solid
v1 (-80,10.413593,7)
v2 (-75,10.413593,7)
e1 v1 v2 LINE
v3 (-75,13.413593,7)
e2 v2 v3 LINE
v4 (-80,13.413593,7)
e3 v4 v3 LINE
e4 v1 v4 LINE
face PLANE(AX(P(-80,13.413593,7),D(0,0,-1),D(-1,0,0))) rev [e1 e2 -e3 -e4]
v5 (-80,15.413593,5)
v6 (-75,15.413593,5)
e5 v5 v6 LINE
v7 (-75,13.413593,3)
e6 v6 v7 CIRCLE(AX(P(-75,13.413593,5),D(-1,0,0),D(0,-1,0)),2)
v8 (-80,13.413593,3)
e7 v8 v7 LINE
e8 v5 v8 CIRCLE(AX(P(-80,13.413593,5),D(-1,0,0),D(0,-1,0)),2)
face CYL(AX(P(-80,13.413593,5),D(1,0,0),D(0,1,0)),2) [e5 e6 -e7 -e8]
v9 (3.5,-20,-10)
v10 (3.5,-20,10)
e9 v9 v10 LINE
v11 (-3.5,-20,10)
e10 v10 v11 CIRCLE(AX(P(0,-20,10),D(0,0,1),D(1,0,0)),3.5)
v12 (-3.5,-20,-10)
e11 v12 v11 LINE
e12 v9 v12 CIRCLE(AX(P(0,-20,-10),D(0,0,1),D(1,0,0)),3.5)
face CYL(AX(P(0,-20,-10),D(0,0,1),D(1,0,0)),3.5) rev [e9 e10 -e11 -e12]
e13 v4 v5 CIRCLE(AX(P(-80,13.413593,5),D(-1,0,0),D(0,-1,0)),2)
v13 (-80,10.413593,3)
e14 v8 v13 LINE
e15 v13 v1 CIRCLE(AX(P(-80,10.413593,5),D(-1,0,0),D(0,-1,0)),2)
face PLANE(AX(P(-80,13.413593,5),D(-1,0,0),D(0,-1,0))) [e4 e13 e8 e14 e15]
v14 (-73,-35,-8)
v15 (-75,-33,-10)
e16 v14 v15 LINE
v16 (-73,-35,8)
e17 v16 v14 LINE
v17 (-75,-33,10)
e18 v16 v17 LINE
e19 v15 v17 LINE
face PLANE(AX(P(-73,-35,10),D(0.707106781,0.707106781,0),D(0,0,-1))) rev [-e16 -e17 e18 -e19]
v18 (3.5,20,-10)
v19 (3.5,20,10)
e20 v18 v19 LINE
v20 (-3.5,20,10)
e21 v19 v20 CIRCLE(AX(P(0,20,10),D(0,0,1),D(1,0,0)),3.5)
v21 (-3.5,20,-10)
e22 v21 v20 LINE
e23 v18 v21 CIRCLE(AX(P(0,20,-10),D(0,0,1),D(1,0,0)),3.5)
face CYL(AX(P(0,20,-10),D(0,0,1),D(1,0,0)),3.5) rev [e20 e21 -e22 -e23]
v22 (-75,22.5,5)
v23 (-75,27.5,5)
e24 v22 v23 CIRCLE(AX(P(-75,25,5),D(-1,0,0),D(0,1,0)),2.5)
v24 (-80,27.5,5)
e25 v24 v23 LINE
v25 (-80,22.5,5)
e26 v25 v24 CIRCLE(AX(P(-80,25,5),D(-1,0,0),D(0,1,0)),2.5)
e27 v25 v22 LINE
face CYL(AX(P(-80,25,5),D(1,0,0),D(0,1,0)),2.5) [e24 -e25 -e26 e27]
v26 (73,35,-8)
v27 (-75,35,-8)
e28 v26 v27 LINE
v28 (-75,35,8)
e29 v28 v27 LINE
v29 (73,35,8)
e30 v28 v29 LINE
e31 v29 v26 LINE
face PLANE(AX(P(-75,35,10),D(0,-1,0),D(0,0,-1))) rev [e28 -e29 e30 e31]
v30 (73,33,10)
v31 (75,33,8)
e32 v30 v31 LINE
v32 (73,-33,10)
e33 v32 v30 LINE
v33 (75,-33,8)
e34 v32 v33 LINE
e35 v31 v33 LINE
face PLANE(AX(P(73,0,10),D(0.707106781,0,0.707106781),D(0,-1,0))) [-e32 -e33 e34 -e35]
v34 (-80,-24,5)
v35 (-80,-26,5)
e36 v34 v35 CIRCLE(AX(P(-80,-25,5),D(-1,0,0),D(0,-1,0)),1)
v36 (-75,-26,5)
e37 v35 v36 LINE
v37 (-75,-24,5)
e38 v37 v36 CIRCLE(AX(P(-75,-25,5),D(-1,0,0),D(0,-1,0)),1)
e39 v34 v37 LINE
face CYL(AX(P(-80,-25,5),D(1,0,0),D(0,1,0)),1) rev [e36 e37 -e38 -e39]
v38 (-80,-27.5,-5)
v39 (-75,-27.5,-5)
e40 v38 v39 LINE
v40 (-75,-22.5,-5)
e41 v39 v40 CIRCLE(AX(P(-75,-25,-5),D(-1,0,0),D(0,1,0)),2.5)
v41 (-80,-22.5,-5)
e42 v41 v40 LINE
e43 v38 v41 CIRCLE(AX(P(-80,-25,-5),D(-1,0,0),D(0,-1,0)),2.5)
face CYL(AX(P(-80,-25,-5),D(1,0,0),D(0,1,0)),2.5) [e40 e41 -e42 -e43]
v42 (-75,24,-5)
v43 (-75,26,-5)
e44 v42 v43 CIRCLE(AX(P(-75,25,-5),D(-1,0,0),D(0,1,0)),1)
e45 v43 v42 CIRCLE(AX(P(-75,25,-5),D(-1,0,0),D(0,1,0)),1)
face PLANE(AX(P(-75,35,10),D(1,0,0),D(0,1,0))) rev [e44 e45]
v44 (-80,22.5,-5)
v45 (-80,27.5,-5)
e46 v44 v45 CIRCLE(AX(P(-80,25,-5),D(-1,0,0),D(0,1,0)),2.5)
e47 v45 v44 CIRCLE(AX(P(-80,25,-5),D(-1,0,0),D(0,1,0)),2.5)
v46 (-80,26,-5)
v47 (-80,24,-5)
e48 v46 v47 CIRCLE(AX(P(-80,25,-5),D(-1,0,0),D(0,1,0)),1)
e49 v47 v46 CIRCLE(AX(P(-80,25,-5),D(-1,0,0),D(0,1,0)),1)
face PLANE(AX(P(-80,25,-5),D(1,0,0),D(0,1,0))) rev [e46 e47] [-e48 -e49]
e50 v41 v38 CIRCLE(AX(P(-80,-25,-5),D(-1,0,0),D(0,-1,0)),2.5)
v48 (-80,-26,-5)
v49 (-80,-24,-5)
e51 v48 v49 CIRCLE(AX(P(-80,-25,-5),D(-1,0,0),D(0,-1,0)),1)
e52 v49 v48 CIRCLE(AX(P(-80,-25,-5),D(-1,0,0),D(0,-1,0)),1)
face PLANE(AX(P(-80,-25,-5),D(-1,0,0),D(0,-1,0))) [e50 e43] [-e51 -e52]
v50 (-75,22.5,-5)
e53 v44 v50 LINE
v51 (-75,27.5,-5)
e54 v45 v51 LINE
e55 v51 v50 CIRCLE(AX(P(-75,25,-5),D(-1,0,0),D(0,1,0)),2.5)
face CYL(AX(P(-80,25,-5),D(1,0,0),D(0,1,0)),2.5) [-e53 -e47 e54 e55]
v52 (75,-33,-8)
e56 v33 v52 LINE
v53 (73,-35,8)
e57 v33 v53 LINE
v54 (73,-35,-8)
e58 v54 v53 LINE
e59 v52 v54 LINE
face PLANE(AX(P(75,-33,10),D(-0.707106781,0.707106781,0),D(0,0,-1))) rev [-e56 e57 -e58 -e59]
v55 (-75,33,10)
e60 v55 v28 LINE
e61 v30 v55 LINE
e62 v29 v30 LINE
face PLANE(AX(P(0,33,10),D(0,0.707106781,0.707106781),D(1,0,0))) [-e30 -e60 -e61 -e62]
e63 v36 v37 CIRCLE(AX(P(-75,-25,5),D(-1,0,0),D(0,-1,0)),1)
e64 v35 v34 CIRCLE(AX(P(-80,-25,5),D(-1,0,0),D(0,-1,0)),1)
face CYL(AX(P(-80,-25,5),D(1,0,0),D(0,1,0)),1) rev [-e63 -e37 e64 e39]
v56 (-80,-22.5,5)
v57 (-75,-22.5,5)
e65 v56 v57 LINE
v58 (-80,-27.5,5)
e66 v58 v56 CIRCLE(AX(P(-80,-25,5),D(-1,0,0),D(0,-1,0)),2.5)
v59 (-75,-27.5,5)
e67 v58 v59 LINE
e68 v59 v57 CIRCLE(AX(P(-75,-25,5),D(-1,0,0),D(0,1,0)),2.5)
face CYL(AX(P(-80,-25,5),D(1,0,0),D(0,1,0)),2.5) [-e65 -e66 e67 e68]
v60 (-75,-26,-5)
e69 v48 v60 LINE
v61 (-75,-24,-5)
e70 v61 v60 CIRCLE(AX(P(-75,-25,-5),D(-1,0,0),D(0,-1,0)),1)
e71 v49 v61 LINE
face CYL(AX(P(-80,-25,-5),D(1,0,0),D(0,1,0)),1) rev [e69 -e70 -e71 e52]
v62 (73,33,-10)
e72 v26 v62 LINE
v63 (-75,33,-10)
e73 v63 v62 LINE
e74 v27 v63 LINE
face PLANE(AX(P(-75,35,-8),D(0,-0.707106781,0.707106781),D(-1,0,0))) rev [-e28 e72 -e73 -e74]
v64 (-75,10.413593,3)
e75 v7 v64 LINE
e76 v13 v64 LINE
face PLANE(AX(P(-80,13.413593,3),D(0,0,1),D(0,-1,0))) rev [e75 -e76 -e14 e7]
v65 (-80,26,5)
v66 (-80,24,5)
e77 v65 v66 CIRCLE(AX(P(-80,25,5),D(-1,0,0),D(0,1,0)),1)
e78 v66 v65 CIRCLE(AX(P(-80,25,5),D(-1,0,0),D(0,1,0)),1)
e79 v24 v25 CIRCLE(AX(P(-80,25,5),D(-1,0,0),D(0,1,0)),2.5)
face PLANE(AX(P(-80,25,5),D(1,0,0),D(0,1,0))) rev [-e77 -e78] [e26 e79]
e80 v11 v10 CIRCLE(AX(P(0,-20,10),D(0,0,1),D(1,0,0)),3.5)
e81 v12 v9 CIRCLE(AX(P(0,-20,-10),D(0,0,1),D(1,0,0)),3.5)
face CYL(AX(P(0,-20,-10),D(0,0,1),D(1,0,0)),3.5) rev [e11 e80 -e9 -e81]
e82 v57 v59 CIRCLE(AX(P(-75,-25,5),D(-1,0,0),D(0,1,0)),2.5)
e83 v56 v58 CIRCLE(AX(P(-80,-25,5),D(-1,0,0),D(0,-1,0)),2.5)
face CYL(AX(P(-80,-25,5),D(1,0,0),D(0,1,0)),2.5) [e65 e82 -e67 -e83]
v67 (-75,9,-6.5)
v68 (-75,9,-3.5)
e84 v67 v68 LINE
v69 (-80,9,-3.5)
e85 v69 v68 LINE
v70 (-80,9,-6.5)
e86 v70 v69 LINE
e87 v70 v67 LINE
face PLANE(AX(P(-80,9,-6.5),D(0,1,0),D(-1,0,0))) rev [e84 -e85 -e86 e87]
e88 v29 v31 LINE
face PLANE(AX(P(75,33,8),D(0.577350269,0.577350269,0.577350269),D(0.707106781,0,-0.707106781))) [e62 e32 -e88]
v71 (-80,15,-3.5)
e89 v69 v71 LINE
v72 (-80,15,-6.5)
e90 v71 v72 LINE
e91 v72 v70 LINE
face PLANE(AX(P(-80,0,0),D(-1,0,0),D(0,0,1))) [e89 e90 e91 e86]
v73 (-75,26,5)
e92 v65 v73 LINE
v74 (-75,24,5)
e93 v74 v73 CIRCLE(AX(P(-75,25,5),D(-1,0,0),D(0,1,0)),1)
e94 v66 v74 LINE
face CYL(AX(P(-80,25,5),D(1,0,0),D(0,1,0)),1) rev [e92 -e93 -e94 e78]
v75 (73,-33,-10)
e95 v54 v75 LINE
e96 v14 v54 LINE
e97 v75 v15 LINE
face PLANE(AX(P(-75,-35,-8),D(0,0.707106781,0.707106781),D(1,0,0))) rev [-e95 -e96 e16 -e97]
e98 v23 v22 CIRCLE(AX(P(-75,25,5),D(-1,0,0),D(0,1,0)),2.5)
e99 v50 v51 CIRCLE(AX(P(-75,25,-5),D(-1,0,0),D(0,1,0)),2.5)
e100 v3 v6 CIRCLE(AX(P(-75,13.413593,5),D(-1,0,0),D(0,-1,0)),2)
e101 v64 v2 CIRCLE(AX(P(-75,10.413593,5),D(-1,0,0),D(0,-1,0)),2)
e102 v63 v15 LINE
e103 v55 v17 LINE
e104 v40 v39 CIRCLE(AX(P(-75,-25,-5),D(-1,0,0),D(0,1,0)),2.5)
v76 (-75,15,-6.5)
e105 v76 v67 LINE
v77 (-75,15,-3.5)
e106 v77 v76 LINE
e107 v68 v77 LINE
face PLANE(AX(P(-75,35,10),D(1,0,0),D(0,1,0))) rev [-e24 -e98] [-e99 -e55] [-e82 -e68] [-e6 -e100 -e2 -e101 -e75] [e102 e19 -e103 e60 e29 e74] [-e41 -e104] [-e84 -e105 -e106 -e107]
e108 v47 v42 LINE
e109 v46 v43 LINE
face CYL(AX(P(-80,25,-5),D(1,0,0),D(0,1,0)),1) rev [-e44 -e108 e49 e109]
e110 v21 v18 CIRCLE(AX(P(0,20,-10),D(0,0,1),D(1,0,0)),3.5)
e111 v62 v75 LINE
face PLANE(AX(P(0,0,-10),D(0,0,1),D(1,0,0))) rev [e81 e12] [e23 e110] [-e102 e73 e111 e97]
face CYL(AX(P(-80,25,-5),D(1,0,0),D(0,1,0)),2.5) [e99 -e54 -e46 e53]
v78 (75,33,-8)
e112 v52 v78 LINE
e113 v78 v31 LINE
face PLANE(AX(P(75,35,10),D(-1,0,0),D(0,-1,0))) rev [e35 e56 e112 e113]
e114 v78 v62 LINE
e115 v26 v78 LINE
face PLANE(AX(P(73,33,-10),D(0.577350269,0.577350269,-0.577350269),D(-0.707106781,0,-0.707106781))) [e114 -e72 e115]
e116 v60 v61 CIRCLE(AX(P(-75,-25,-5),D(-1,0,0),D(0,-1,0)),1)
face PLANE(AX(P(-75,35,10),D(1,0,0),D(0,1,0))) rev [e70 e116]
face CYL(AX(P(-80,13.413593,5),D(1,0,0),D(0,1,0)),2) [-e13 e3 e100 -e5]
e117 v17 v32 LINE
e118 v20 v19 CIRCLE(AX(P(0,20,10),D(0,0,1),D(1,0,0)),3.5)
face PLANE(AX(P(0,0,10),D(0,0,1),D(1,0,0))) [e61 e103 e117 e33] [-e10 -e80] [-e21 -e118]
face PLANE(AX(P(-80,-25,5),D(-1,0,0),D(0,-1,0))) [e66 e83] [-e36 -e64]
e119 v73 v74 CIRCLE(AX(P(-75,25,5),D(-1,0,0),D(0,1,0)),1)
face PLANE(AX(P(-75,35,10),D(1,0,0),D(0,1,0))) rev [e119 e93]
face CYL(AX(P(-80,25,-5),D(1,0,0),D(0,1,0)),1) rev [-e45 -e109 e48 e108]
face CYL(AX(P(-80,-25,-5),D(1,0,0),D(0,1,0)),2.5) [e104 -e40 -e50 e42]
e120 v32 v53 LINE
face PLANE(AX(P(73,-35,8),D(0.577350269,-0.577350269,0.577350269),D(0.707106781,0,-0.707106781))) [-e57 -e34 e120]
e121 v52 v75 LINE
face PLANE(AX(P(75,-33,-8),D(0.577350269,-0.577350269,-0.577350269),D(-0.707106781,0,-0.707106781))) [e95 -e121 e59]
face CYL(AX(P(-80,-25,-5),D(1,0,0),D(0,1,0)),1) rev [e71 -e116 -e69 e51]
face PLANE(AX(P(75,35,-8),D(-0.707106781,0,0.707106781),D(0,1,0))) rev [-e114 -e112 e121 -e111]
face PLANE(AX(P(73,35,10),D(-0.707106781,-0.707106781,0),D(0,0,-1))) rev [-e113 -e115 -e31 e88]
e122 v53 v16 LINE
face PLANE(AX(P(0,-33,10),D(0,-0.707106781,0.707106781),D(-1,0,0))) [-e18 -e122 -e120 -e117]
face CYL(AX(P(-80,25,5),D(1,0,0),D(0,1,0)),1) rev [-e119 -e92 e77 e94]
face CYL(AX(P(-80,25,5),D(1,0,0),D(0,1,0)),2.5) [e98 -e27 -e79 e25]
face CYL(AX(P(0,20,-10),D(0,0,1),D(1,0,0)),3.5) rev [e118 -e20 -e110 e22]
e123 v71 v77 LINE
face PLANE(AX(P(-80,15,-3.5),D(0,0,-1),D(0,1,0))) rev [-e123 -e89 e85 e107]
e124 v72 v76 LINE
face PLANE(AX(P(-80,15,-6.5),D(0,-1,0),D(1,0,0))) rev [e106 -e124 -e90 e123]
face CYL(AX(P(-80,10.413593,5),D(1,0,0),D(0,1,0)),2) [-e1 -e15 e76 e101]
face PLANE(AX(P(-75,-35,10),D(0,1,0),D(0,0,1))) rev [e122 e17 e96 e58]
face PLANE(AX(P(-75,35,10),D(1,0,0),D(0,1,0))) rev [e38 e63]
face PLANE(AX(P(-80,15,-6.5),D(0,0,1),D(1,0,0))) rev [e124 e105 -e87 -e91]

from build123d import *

# Parameters (mm, degrees)
SKETCH2_W           = 150
SKETCH2_H           = 70
BOSS_EXTRUDE1_DEPTH = 10
SKETCH3_R           = 2.5
SKETCH3_R_2         = 1
SKETCH3_W           = 3
SKETCH3_H           = 6
BOSS_EXTRUDE2_DEPTH = 5
CHAMFER1_SIZE       = 2
SKETCH4_R           = 3.5
CUT_EXTRUDE1_DEPTH  = 90.582364336


with BuildPart() as part:
    # Sketch2 → Boss-Extrude1 (new, symmetric)
    with BuildSketch(Plane.XY):
        Rectangle(SKETCH2_W, SKETCH2_H)
    extrude(amount=BOSS_EXTRUDE1_DEPTH, both=True)

    # Sketch3 → Boss-Extrude2 (add)
    # profile 1 of 6: a face of its own
    with BuildSketch(Plane.ZY.offset(75)):
        with Locations(Location((-5, -25, 0), (0, 0, 90))):
            Circle(SKETCH3_R)
        with Locations(Location((-5, -25, 0), (0, 0, 270))):
            Circle(SKETCH3_R_2, mode=Mode.SUBTRACT)
    # profile 2 of 6: a face of its own
    with BuildSketch(Plane.ZY.offset(75)):
        with Locations(Location((5, -25, 0), (0, 0, 90))):
            Circle(SKETCH3_R)
        with Locations(Location((5, -25, 0), (0, 0, 270))):
            Circle(SKETCH3_R_2, mode=Mode.SUBTRACT)
    # profile 3 of 6: a face of its own
    with BuildSketch(Plane.ZY.offset(75)):
        with Locations(Location((5, 25, 0), (0, 0, 90))):
            Circle(SKETCH3_R)
        with Locations(Location((5, 25, 0), (0, 0, 90))):
            Circle(SKETCH3_R_2, mode=Mode.SUBTRACT)
    # profile 4 of 6: a face of its own
    with BuildSketch(Plane.ZY.offset(75)):
        with Locations(Location((-5, 25, 0), (0, 0, 90))):
            Circle(SKETCH3_R)
        with Locations(Location((-5, 25, 0), (0, 0, 90))):
            Circle(SKETCH3_R_2, mode=Mode.SUBTRACT)
    # profile 5 of 6: a face of its own
    with BuildSketch(Plane.ZY.offset(75)):
        with BuildLine():
            Line((7, 13.4135929), (7, 10.4135929))
            ThreePointArc((7, 10.4135929), (5, 8.4135929), (3, 10.4135929))
            Line((3, 10.4135929), (3, 13.4135929))
            ThreePointArc((3, 13.4135929), (5, 15.4135929), (7, 13.4135929))
        make_face()
    # profile 6 of 6: a face of its own
    with BuildSketch(Plane.ZY.offset(75)):
        with Locations((-5, 12)):
            Rectangle(SKETCH3_W, SKETCH3_H)
    extrude(amount=BOSS_EXTRUDE2_DEPTH)

    # Chamfer1
    chamfer1_edges = [part.edges().sort_by_distance(p)[0] for p in [
        (0, -35, 10),
        (75, 0, 10),
        (0, -35, -10),
        (0, 35, -10),
        (75, 0, -10),
        (75, -35, 0),
        (-75, -35, 0),
        (75, 35, 0),
        (0, 35, 10),
    ]]
    chamfer(chamfer1_edges, length=CHAMFER1_SIZE)

    # Sketch4 → Cut-Extrude1 (cut, through all)
    with BuildSketch(Plane.XY.offset(10)):
        with Locations((0, 20)):
            Circle(SKETCH4_R)
        with Locations((0, -20)):
            Circle(SKETCH4_R)
    extrude(amount=-CUT_EXTRUDE1_DEPTH, mode=Mode.SUBTRACT)


solid = part.part
